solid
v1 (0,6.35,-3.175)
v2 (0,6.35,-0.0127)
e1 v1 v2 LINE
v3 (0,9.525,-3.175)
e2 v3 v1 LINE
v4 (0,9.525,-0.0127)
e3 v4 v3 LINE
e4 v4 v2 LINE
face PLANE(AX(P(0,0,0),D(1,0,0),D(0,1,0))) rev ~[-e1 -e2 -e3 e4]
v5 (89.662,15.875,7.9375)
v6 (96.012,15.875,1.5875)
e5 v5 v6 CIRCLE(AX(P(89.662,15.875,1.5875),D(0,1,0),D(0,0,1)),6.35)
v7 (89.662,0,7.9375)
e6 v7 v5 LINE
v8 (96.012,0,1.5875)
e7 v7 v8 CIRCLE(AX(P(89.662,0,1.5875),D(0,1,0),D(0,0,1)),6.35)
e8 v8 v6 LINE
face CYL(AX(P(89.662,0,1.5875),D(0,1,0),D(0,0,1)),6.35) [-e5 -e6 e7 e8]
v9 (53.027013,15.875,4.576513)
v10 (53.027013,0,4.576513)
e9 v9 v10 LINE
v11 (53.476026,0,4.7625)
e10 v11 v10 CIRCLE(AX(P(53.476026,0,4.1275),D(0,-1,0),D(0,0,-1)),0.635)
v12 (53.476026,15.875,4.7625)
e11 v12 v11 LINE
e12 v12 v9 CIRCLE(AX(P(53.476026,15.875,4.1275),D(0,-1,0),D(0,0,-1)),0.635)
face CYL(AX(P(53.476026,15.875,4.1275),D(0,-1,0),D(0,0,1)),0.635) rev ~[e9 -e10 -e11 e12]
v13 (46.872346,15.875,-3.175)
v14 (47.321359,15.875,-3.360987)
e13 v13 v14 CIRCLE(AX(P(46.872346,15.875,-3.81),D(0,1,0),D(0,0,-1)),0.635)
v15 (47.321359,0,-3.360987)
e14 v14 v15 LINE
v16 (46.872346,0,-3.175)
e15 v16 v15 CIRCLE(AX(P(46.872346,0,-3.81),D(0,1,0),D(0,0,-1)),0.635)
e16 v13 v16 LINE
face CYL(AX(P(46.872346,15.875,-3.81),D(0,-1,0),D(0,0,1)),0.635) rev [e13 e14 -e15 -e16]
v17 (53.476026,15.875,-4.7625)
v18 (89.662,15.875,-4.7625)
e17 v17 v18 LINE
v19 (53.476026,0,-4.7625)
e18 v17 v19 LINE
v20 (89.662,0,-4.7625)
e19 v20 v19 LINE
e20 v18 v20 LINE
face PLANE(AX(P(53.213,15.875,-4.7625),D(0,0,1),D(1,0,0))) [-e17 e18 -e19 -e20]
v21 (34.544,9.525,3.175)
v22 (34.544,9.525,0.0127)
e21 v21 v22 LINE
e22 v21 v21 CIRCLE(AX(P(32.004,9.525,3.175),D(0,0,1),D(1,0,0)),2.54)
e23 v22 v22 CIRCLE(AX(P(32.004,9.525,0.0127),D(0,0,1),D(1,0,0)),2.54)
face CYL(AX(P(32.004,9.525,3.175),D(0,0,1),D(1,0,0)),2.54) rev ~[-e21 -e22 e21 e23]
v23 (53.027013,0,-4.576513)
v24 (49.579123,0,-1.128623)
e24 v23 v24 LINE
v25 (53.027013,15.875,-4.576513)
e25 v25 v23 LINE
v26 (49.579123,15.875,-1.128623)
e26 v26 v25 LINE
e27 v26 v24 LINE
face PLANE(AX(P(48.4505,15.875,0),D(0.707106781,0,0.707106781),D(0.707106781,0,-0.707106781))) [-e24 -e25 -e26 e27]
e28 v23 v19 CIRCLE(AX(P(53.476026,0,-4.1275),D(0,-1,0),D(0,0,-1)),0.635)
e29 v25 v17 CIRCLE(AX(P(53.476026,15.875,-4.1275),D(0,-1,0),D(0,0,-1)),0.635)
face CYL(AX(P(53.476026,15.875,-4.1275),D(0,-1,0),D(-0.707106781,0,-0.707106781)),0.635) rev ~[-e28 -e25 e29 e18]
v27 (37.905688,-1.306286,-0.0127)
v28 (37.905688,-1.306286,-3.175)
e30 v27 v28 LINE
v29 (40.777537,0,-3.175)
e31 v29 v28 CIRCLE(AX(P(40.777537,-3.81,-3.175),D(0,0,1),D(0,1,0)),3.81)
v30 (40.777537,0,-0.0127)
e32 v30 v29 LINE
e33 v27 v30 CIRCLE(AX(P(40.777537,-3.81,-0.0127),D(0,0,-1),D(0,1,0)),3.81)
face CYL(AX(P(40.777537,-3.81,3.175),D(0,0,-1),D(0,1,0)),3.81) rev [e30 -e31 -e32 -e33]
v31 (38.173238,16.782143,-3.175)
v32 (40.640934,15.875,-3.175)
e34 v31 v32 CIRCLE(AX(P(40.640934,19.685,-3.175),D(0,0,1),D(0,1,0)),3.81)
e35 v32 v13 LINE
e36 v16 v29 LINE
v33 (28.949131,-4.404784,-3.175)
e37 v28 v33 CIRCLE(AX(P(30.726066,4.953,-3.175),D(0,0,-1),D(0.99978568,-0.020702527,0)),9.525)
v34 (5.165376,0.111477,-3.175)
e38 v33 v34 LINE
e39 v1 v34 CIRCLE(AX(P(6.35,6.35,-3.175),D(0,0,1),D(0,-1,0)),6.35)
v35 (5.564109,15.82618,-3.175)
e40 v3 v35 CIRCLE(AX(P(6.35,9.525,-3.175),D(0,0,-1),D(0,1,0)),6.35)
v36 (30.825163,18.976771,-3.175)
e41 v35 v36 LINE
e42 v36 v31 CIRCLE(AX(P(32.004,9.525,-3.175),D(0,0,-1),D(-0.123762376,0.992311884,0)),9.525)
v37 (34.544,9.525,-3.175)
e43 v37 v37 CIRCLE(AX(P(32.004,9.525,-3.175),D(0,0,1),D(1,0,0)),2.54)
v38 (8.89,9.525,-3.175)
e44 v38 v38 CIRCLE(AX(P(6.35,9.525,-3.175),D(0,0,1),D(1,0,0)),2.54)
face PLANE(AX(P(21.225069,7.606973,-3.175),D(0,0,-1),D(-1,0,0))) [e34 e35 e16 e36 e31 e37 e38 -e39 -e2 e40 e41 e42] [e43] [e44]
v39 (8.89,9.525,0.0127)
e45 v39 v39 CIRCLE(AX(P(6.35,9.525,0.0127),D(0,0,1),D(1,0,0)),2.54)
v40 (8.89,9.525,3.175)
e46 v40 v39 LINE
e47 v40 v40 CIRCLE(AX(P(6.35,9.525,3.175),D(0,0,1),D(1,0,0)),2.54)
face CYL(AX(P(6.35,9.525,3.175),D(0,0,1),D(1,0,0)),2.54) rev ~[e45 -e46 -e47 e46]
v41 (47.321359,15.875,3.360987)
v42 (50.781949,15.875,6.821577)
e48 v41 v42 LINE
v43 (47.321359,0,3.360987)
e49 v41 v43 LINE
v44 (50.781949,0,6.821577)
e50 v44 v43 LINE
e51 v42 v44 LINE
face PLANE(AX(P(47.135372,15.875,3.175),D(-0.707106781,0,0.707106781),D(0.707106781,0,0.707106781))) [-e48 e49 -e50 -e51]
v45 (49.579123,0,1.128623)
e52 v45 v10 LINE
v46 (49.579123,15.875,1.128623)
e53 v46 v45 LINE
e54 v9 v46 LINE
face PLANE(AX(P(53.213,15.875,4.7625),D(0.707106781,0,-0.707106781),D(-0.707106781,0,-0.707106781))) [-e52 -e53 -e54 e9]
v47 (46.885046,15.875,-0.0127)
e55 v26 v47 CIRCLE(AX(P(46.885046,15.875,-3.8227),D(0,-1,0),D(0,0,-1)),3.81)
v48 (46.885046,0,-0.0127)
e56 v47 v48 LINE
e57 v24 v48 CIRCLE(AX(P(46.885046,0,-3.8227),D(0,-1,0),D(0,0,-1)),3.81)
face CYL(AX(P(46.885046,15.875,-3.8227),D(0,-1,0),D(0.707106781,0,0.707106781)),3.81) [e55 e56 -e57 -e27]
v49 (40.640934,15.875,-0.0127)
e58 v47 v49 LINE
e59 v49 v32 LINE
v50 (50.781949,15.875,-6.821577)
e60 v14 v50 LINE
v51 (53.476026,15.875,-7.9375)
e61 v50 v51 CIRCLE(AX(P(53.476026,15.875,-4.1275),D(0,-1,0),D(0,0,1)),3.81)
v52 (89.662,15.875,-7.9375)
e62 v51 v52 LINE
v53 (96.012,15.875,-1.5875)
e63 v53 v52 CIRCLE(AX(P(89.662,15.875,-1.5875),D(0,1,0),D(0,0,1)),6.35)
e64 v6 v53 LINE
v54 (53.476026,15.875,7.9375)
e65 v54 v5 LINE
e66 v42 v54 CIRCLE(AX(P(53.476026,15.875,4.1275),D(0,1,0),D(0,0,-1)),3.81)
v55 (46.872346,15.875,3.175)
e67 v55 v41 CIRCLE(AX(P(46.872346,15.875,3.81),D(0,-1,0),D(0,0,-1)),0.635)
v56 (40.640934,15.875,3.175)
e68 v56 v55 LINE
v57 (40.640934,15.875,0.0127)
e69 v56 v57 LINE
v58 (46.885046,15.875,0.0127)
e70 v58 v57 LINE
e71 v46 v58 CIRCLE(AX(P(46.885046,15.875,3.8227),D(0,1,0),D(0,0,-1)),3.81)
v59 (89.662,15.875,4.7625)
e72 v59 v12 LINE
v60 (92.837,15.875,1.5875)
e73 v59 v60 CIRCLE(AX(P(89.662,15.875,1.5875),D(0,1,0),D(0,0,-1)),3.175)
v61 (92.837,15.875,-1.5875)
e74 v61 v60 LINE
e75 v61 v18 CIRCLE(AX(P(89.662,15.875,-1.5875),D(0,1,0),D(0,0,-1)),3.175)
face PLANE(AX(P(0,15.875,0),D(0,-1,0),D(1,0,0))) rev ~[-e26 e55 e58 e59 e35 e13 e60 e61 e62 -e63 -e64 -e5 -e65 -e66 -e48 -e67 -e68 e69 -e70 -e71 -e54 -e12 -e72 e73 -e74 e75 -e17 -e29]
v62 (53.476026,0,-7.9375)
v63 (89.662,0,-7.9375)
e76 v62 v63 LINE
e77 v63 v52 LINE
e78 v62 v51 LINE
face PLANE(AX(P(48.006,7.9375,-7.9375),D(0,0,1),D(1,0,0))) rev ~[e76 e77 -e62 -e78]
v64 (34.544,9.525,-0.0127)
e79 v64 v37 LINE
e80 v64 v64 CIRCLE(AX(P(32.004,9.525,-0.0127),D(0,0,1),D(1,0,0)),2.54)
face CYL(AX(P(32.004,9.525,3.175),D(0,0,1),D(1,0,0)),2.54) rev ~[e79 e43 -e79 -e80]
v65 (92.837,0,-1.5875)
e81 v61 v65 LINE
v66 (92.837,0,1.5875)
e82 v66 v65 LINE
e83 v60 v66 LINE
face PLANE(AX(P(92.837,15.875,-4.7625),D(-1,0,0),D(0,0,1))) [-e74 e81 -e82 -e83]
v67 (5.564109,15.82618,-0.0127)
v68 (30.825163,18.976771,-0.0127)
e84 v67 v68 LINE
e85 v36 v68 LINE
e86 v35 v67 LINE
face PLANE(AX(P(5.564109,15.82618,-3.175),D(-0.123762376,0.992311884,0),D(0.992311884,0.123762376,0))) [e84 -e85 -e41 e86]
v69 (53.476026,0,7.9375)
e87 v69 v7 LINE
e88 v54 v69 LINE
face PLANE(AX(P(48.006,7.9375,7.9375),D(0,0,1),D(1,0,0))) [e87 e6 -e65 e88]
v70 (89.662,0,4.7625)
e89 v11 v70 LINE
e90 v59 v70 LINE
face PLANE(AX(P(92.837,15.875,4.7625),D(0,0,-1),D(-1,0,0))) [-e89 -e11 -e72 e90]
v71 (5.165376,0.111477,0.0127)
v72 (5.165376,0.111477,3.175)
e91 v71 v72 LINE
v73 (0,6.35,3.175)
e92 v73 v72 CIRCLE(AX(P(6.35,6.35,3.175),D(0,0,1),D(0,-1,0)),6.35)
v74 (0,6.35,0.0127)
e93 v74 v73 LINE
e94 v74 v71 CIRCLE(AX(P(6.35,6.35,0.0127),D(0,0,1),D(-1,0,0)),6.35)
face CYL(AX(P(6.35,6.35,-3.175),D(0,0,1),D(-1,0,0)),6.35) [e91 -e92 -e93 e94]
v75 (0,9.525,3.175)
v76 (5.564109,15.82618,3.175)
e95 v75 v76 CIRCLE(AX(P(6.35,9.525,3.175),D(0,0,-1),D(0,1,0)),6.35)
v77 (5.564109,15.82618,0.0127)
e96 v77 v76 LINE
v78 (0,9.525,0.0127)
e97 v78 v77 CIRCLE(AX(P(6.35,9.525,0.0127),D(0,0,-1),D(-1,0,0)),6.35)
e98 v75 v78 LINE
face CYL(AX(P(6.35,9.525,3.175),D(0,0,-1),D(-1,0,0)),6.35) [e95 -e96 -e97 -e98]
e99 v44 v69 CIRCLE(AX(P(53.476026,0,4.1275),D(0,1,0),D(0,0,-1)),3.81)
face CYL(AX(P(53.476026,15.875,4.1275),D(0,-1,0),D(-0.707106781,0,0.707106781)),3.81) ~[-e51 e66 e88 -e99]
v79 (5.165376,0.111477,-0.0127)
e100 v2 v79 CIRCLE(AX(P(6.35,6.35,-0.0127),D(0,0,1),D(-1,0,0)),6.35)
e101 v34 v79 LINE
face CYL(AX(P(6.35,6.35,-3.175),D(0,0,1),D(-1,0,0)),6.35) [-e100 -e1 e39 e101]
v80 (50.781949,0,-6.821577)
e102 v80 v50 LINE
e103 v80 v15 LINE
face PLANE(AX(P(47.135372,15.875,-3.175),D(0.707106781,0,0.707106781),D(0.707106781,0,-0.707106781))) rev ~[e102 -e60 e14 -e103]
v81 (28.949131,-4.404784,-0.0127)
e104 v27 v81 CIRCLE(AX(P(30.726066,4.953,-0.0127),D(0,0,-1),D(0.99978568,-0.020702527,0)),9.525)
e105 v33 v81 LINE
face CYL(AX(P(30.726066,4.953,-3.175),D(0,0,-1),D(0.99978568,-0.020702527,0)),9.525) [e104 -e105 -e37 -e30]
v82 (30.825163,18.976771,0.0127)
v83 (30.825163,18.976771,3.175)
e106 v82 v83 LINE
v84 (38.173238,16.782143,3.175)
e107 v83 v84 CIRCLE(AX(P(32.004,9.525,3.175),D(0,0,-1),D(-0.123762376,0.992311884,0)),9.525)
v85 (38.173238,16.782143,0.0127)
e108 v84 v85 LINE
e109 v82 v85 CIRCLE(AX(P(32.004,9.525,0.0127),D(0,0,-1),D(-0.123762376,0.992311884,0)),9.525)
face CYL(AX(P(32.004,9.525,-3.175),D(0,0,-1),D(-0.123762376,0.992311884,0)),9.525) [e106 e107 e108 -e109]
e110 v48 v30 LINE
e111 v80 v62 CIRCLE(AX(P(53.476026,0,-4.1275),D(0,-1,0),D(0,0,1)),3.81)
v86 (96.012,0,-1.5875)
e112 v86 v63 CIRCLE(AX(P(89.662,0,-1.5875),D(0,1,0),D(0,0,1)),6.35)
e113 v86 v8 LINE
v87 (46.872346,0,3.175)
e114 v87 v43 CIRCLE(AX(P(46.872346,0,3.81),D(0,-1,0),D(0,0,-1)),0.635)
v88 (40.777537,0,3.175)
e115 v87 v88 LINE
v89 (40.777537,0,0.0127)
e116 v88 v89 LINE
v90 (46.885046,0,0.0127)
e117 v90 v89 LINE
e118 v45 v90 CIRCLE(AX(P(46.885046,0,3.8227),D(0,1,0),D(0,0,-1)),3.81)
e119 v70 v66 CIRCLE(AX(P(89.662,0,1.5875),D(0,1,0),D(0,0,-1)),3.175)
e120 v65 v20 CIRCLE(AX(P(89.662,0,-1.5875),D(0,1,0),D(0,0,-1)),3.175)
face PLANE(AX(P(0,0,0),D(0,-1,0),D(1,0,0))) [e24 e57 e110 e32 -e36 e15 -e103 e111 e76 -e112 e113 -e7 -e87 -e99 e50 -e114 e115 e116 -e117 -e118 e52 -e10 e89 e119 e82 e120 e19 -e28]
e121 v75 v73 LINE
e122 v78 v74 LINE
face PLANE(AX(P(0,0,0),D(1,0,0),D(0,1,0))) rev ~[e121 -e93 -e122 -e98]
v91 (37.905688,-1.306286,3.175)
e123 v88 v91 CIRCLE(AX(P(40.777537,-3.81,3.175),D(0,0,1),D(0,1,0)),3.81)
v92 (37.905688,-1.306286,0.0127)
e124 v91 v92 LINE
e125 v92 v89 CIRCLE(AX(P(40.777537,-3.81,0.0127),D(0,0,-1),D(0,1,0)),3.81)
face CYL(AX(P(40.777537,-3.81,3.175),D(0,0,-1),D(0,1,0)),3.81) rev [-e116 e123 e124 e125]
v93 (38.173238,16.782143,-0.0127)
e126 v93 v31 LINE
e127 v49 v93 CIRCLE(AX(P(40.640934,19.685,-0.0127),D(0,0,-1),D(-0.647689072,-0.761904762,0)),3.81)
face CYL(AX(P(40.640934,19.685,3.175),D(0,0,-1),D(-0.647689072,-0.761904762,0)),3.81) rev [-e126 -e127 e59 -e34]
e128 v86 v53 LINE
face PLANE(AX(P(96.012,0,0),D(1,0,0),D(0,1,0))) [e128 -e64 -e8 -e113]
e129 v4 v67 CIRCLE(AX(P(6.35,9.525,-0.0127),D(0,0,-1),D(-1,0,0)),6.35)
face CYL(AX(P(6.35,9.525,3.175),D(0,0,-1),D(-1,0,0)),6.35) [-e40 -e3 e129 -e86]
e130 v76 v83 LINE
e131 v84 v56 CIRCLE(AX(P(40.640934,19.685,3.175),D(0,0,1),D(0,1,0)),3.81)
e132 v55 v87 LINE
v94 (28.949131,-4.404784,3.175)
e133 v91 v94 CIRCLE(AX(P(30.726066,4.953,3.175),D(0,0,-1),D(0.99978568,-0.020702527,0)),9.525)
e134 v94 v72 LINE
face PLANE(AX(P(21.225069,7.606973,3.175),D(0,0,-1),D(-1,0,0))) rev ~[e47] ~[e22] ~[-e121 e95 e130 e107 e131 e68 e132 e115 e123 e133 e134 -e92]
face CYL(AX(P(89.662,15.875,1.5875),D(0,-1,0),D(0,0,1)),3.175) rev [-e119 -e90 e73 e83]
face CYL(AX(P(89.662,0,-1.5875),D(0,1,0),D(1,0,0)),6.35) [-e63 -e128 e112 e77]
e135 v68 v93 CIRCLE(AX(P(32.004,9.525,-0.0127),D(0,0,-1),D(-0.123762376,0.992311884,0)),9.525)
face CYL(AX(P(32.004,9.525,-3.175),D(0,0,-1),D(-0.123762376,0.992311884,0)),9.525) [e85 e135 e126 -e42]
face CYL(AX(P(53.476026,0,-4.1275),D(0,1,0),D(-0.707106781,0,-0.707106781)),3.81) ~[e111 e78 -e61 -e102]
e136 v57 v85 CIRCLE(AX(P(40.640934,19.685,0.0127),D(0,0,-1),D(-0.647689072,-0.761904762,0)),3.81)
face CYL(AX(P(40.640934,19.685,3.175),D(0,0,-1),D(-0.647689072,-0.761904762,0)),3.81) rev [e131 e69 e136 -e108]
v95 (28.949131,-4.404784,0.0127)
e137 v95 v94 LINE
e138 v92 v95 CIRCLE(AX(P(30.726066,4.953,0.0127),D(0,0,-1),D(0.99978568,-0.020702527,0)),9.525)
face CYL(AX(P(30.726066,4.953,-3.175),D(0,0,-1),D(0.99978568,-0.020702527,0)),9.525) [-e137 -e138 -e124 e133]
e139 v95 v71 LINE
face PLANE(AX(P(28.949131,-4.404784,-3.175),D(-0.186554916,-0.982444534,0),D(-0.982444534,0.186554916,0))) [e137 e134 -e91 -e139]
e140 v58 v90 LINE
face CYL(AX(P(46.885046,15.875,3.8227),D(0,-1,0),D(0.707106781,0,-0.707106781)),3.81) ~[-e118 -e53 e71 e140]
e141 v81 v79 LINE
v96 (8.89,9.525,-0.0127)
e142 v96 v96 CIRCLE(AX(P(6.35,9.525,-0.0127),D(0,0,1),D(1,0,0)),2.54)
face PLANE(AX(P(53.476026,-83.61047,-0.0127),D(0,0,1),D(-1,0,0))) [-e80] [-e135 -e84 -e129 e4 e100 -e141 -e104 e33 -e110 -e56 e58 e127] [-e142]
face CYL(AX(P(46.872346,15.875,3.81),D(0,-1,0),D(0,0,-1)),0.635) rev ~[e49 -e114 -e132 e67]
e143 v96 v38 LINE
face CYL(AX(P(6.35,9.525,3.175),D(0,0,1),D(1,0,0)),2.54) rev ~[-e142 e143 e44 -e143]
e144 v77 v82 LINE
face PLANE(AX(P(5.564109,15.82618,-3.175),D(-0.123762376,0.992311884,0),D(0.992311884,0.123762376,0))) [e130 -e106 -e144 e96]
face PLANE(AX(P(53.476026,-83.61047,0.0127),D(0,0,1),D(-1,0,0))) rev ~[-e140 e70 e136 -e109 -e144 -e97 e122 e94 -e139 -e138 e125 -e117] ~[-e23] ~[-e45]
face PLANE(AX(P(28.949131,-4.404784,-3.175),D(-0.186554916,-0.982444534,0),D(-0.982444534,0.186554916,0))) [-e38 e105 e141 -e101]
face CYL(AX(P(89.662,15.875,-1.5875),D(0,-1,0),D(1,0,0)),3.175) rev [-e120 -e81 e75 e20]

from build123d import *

# Parameters (mm, degrees)
SKETCH1_W               = 96.012
SKETCH1_H               = 15.875
BASE_EXTRUDE_DEPTH      = 7.9375
CUT_EXTRUDE1_DEPTH      = 98.638740648
FILLET5_R               = 0.635
FILLET6_R               = 3.81
FILLET7_R               = 3.175
FILLET8_R               = 6.35
FILLET9_R               = 6.35
FILLET10_R              = 6.35
BOSS_EXTRUDE3_START     = -6.35
BOSS_EXTRUDE3_DEPTH     = 6.35
FILLET11_R              = 3.81
SKETCH7_R               = 2.54
CUT_EXTRUDE5_DEPTH      = 99.512406834
CUT_EXTRUDE6_DEPTH      = 99.485470295
CUT_EXTRUDE6_DEPTH_BACK = 99.485470295
SKETCH8_W               = 56.651025612
SKETCH8_H               = 0.0254
FILLET12_R              = 3.81
FILLET13_R              = 3.81


with BuildPart() as part:
    # Sketch1 → Base-Extrude (new, symmetric)
    with BuildSketch(Plane.XY):
        with Locations((48.006, 7.9375)):
            Rectangle(SKETCH1_W, SKETCH1_H)
    extrude(amount=BASE_EXTRUDE_DEPTH, both=True)

    # Sketch3 → Cut-Extrude1 (cut, through all)
    with BuildSketch(Plane(origin=(0, 15.875, 0), x_dir=(-1, 0, 0), z_dir=(0, 1, 0))):
        Polygon((-53.213, -4.7625), (-92.837, -4.7625), (-92.837, 4.7625), (-53.213, 4.7625), (-48.4505, 0), align=None)
        Polygon((2.11806403, -3.175), (-47.135371939, -3.175), (-55.848364541, -11.887992602), (2.11806403, -11.887992602), align=None)
        Polygon((2.11806403, 3.175), (-47.135371939, 3.175), (-55.848364541, 11.887992602), (2.11806403, 11.887992602), align=None)
    extrude(amount=-CUT_EXTRUDE1_DEPTH, mode=Mode.SUBTRACT)

    # Fillet5
    fillet5_edges = [part.edges().sort_by_distance(p)[0] for p in [
        (53.213, 7.9375, -4.7625),
        (53.213, 7.9375, 4.7625),
        (47.135371939, 7.9375, 3.175),
        (47.135371939, 7.9375, -3.175),
    ]]
    fillet(fillet5_edges, radius=FILLET5_R)

    # Fillet6
    fillet6_edges = [part.edges().sort_by_distance(p)[0] for p in [
        (51.897871939, 7.9375, 7.9375),
        (51.897871939, 7.9375, -7.9375),
    ]]
    fillet(fillet6_edges, radius=FILLET6_R)

    # Fillet7
    fillet7_edges = [part.edges().sort_by_distance(p)[0] for p in [
        (92.837, 7.9375, -4.7625),
        (92.837, 7.9375, 4.7625),
    ]]
    fillet(fillet7_edges, radius=FILLET7_R)

    # Fillet8
    fillet8_edges = [part.edges().sort_by_distance(p)[0] for p in [
        (96.012, 7.9375, 7.9375),
        (96.012, 7.9375, -7.9375),
    ]]
    fillet(fillet8_edges, radius=FILLET8_R)

    # Fillet9
    fillet9_edges = [part.edges().sort_by_distance(p)[0] for p in [
        (0, 15.875, 0),
    ]]
    fillet(fillet9_edges, radius=FILLET9_R)

    # Fillet10
    fillet10_edges = [part.edges().sort_by_distance(p)[0] for p in [
        (0, 0, 0),
    ]]
    fillet(fillet10_edges, radius=FILLET10_R)

    # Sketch6 → Boss-Extrude3 (add)
    with BuildSketch(Plane.XY.offset(3.175).offset(BOSS_EXTRUDE3_START)):
        with BuildLine():
            Line((5.564108911, 15.826180461), (30.825163366, 18.976770691))
            ThreePointArc((30.825163366, 18.976770691), (39.943880119, 14.786551928), (40.249024971, 4.755808431))
            ThreePointArc((40.249024971, 4.755808431), (36.72434383, -2.446073762), (28.949130797, -4.404784191))
            Line((28.949130797, -4.404784191), (5.165376283, 0.111477206))
            ThreePointArc((5.165376283, 0.111477206), (1.458943846, 2.300300048), (0, 6.35))
            Line((0, 6.35), (0, 9.525))
            ThreePointArc((0, 9.525), (1.590120358, 13.728099546), (5.564108911, 15.826180461))
        make_face()
    extrude(amount=BOSS_EXTRUDE3_DEPTH)

    # Fillet11
    fillet11_edges = [part.edges().sort_by_distance(p)[0] for p in [
        (38.862, 0, 0),
        (39.103515829, 15.875, 0),
    ]]
    fillet(fillet11_edges, radius=FILLET11_R)

    # Sketch7 → Cut-Extrude5 (cut, through all)
    with BuildSketch(Plane.XY.offset(3.175)):
        with Locations((6.35, 9.525)):
            Circle(SKETCH7_R)
        with Locations((32.004, 9.525)):
            Circle(SKETCH7_R)
    extrude(amount=-CUT_EXTRUDE5_DEPTH, mode=Mode.SUBTRACT)

    # Sketch8 → Cut-Extrude6 (cut, two sides: drawn at the far end of the back side and taken through both)
    with BuildSketch(Plane(origin=(0, 15.875, 0), x_dir=(-1, 0, 0), z_dir=(0, 1, 0)).offset(-CUT_EXTRUDE6_DEPTH_BACK)):
        with Locations((-25.150512806, 0)):
            Rectangle(SKETCH8_W, SKETCH8_H)
    extrude(amount=CUT_EXTRUDE6_DEPTH + CUT_EXTRUDE6_DEPTH_BACK, mode=Mode.SUBTRACT)

    # Fillet12
    fillet12_edges = [part.edges().sort_by_distance(p)[0] for p in [
        (48.4632, 7.9375, 0.0127),
    ]]
    fillet(fillet12_edges, radius=FILLET12_R)

    # Fillet13
    fillet13_edges = [part.edges().sort_by_distance(p)[0] for p in [
        (48.4632, 7.9375, -0.0127),
    ]]
    fillet(fillet13_edges, radius=FILLET13_R)


solid = part.part
